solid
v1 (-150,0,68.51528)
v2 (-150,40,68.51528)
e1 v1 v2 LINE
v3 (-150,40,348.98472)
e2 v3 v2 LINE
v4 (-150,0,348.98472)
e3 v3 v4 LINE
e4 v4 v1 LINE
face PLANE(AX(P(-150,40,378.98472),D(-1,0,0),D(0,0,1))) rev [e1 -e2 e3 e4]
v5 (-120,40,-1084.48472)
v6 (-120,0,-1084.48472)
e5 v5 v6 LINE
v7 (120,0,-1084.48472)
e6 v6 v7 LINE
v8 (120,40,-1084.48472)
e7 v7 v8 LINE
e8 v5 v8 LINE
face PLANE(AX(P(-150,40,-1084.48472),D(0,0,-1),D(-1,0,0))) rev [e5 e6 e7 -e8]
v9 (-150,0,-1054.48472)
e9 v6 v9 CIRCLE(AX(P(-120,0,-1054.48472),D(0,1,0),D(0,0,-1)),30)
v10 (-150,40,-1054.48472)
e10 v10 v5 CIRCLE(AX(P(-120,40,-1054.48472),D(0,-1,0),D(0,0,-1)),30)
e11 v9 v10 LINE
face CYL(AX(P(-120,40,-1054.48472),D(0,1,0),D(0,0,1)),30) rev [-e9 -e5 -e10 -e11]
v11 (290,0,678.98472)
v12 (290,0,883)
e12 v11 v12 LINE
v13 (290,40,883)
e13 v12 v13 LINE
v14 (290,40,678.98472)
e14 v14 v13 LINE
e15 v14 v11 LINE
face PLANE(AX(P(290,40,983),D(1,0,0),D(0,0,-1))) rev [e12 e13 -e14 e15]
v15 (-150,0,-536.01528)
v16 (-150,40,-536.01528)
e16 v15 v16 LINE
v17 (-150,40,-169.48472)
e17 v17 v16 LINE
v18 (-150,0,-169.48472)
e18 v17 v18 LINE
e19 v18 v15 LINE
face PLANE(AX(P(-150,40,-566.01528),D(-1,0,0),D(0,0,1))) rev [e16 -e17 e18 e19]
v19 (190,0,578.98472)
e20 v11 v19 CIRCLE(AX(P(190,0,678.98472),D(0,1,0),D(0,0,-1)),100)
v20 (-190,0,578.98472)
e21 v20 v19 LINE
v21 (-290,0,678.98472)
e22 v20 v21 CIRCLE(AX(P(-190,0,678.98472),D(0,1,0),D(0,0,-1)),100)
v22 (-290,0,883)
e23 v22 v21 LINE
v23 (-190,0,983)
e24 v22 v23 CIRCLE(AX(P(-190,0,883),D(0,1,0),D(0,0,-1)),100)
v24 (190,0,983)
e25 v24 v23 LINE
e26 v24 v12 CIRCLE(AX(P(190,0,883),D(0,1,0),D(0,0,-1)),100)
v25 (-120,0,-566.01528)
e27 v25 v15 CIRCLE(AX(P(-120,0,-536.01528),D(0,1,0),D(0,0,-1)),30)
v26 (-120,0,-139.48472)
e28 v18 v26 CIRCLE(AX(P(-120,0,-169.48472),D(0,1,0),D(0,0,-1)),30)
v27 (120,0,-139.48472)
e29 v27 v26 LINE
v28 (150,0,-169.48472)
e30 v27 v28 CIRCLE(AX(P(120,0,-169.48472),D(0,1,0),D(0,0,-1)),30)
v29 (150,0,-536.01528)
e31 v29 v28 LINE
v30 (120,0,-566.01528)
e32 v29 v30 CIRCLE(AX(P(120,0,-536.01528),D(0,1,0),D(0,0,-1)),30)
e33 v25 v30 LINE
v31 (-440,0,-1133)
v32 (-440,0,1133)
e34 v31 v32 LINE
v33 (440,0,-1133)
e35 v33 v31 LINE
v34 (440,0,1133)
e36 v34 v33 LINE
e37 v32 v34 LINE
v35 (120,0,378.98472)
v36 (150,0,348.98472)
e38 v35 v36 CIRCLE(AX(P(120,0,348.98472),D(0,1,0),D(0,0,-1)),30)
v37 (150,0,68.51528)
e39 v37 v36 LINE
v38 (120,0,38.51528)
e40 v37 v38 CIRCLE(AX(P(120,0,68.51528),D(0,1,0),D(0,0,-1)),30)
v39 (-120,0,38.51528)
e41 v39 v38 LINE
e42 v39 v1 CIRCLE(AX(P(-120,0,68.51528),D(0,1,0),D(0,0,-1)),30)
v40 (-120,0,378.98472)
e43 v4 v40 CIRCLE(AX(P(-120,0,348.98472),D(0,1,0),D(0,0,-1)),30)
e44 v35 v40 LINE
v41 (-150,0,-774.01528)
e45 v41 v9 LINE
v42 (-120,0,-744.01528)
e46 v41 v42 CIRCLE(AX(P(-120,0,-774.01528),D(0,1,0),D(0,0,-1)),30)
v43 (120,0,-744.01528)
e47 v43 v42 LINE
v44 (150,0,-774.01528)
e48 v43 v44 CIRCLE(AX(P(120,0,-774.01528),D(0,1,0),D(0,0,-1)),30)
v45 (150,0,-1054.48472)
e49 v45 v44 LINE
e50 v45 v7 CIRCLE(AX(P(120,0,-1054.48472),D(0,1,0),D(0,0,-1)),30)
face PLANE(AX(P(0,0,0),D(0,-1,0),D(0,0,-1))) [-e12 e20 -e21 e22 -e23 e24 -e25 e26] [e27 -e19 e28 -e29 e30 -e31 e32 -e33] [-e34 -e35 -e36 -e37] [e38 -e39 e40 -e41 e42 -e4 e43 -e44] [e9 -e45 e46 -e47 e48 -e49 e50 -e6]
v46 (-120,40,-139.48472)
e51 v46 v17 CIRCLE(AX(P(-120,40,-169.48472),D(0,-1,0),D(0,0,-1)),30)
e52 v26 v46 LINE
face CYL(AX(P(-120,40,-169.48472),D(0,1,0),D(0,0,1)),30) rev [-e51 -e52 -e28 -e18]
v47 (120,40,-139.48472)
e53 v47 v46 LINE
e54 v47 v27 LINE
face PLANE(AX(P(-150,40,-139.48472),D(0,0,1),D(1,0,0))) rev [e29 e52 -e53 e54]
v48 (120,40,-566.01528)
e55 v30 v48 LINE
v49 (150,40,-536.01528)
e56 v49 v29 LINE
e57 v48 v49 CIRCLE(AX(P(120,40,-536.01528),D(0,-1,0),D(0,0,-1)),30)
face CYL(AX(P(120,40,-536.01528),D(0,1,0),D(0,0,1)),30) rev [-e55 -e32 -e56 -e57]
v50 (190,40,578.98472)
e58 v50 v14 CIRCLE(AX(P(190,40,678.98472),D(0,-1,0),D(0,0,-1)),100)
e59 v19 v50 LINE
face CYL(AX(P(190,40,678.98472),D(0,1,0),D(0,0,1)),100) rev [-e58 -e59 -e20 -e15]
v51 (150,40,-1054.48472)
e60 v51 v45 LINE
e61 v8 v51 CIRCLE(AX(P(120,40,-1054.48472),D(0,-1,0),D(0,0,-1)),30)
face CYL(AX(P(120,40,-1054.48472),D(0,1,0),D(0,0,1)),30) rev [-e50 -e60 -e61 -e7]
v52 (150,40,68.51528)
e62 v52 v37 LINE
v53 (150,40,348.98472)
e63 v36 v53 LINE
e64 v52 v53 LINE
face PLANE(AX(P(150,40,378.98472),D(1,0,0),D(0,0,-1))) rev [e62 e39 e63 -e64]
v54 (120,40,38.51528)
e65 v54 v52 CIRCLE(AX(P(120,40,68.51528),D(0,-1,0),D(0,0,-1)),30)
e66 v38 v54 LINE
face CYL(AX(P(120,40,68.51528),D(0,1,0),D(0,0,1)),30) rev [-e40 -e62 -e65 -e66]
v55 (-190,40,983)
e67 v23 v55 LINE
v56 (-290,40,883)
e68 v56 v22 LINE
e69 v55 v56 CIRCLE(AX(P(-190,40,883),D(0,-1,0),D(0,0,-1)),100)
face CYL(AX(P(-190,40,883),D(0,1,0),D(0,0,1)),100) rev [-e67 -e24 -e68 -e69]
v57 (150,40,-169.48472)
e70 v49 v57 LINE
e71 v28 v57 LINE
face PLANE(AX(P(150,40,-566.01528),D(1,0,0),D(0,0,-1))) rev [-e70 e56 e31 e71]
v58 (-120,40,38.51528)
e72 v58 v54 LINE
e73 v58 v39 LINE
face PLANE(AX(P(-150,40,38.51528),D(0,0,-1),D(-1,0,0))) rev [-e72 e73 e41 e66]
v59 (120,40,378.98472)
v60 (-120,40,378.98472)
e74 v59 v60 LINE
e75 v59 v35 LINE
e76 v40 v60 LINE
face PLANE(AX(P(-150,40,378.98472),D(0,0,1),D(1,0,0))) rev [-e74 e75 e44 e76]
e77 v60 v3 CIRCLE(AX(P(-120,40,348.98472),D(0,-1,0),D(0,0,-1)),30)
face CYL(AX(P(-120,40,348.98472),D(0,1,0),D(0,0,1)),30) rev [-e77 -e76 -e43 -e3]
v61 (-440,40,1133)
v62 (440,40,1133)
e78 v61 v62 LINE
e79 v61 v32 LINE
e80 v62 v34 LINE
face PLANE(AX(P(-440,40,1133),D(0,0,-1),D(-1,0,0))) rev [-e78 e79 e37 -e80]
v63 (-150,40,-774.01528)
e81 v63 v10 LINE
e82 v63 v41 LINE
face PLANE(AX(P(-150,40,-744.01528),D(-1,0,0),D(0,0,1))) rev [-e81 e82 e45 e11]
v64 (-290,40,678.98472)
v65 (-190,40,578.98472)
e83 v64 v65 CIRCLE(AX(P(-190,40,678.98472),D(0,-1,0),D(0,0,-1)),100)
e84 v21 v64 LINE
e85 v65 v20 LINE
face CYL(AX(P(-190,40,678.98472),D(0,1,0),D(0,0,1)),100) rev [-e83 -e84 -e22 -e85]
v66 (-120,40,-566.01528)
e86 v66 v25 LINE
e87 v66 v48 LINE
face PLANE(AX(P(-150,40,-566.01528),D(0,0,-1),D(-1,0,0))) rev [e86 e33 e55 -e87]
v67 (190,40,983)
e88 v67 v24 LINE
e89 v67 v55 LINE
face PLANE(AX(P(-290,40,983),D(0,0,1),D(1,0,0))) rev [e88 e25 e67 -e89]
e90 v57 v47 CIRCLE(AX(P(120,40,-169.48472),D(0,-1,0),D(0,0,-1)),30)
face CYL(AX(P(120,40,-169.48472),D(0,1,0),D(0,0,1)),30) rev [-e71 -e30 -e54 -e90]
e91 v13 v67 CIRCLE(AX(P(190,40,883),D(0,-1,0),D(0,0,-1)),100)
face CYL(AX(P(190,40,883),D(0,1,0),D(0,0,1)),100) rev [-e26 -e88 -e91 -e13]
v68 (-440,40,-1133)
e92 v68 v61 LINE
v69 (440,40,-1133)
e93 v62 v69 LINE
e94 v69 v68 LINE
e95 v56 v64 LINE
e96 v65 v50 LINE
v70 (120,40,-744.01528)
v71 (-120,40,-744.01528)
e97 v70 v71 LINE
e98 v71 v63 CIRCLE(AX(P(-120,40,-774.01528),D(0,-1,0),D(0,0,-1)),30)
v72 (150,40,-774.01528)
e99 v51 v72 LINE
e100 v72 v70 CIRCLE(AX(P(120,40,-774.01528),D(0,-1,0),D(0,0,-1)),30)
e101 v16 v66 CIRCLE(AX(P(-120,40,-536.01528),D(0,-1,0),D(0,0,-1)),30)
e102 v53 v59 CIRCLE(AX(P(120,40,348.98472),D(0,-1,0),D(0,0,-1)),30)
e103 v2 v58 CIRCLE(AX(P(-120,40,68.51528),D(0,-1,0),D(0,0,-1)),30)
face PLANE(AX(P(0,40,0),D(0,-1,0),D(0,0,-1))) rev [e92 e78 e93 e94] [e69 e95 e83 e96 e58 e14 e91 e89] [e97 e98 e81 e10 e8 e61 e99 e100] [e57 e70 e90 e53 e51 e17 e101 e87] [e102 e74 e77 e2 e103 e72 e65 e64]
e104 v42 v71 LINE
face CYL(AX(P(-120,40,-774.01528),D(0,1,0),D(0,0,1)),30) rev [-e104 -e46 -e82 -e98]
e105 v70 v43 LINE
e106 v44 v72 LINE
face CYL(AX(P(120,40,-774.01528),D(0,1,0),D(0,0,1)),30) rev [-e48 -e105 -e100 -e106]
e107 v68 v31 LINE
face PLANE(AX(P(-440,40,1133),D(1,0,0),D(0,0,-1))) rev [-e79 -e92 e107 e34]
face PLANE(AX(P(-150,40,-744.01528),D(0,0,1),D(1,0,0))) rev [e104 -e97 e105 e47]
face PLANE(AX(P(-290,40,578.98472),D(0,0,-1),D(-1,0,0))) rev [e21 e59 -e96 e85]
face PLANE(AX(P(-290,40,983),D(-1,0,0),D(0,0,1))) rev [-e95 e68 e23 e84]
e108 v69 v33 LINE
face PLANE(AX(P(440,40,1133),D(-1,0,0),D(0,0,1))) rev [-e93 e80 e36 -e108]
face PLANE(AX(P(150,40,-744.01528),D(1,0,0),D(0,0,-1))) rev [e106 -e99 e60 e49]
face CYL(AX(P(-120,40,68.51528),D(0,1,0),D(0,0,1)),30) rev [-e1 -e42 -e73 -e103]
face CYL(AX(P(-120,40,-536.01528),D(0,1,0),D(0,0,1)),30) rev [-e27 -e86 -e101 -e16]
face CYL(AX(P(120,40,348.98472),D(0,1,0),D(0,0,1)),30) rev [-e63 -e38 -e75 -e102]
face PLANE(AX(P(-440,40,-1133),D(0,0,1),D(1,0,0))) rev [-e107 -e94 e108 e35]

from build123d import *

# Parameters (mm, degrees)
SKETCH_1_W          = 880
SKETCH_1_H          = 2266
EXTRUDE_1_DEPTH     = 40
SKETCH_2_W          = 300
SKETCH_2_H          = 340.469439268
CUT_EXTRUDE_1_DEPTH = 1217.095802147
SKETCH_3_W          = 300
SKETCH_3_H          = 426.530560732
CUT_EXTRUDE_2_DEPTH = 1217.095802147
SKETCH_4_W          = 300
SKETCH_4_H          = 340.469439268
CUT_EXTRUDE_3_DEPTH = 1217.095802147
SKETCH_5_W          = 580
SKETCH_5_H          = 404.015280366
CUT_EXTRUDE_4_DEPTH = 1217.095802147
FILLET_2_R          = 100
FILLET_3_R          = 30


with BuildPart() as part:
    # 草图1 → 凸台-拉伸1 (new body)
    with BuildSketch(Plane(origin=(0, 0, 0), x_dir=(1, 0, 0), z_dir=(0, 1, 0))):
        Rectangle(SKETCH_1_W, SKETCH_1_H)
    extrude(amount=EXTRUDE_1_DEPTH)

    # 草图2 → 切除-拉伸1 (cut, through all)
    with BuildSketch(Plane.XZ):
        with Locations((0, 208.75)):
            Rectangle(SKETCH_2_W, SKETCH_2_H)
    extrude(amount=-CUT_EXTRUDE_1_DEPTH, mode=Mode.SUBTRACT)

    # 草图3 → 切除-拉伸2 (cut, through all)
    with BuildSketch(Plane.XZ):
        with Locations((0, -352.75)):
            Rectangle(SKETCH_3_W, SKETCH_3_H)
    extrude(amount=-CUT_EXTRUDE_2_DEPTH, mode=Mode.SUBTRACT)

    # 草图4 → 切除-拉伸3 (cut, through all)
    with BuildSketch(Plane(origin=(0, 0, 0), x_dir=(-1, 0, 0), z_dir=(0, -1, 0))):
        with Locations((0, 914.25)):
            Rectangle(SKETCH_4_W, SKETCH_4_H)
    extrude(amount=-CUT_EXTRUDE_3_DEPTH, mode=Mode.SUBTRACT)

    # 草图5 → 切除-拉伸4 (cut, through all)
    with BuildSketch(Plane.XZ):
        with Locations((0, 780.992359817)):
            Rectangle(SKETCH_5_W, SKETCH_5_H)
    extrude(amount=-CUT_EXTRUDE_4_DEPTH, mode=Mode.SUBTRACT)

    # 圆角2
    fillet_2_edges = [part.edges().sort_by_distance(p)[0] for p in [
        (-290, 20, 578.984719634),
        (-290, 20, 983),
        (290, 20, 983),
        (290, 20, 578.984719634),
    ]]
    fillet(fillet_2_edges, radius=FILLET_2_R)

    # 圆角3
    fillet_3_edges = [part.edges().sort_by_distance(p)[0] for p in [
        (-150, 20, 38.515280366),
        (-150, 20, 378.984719634),
        (150, 20, 378.984719634),
        (150, 20, 38.515280366),
        (-150, 20, -566.015280366),
        (-150, 20, -139.484719634),
        (150, 20, -139.484719634),
        (150, 20, -566.015280366),
        (-150, 20, -1084.484719634),
        (-150, 20, -744.015280366),
        (150, 20, -744.015280366),
        (150, 20, -1084.484719634),
    ]]
    fillet(fillet_3_edges, radius=FILLET_3_R)


solid = part.part
